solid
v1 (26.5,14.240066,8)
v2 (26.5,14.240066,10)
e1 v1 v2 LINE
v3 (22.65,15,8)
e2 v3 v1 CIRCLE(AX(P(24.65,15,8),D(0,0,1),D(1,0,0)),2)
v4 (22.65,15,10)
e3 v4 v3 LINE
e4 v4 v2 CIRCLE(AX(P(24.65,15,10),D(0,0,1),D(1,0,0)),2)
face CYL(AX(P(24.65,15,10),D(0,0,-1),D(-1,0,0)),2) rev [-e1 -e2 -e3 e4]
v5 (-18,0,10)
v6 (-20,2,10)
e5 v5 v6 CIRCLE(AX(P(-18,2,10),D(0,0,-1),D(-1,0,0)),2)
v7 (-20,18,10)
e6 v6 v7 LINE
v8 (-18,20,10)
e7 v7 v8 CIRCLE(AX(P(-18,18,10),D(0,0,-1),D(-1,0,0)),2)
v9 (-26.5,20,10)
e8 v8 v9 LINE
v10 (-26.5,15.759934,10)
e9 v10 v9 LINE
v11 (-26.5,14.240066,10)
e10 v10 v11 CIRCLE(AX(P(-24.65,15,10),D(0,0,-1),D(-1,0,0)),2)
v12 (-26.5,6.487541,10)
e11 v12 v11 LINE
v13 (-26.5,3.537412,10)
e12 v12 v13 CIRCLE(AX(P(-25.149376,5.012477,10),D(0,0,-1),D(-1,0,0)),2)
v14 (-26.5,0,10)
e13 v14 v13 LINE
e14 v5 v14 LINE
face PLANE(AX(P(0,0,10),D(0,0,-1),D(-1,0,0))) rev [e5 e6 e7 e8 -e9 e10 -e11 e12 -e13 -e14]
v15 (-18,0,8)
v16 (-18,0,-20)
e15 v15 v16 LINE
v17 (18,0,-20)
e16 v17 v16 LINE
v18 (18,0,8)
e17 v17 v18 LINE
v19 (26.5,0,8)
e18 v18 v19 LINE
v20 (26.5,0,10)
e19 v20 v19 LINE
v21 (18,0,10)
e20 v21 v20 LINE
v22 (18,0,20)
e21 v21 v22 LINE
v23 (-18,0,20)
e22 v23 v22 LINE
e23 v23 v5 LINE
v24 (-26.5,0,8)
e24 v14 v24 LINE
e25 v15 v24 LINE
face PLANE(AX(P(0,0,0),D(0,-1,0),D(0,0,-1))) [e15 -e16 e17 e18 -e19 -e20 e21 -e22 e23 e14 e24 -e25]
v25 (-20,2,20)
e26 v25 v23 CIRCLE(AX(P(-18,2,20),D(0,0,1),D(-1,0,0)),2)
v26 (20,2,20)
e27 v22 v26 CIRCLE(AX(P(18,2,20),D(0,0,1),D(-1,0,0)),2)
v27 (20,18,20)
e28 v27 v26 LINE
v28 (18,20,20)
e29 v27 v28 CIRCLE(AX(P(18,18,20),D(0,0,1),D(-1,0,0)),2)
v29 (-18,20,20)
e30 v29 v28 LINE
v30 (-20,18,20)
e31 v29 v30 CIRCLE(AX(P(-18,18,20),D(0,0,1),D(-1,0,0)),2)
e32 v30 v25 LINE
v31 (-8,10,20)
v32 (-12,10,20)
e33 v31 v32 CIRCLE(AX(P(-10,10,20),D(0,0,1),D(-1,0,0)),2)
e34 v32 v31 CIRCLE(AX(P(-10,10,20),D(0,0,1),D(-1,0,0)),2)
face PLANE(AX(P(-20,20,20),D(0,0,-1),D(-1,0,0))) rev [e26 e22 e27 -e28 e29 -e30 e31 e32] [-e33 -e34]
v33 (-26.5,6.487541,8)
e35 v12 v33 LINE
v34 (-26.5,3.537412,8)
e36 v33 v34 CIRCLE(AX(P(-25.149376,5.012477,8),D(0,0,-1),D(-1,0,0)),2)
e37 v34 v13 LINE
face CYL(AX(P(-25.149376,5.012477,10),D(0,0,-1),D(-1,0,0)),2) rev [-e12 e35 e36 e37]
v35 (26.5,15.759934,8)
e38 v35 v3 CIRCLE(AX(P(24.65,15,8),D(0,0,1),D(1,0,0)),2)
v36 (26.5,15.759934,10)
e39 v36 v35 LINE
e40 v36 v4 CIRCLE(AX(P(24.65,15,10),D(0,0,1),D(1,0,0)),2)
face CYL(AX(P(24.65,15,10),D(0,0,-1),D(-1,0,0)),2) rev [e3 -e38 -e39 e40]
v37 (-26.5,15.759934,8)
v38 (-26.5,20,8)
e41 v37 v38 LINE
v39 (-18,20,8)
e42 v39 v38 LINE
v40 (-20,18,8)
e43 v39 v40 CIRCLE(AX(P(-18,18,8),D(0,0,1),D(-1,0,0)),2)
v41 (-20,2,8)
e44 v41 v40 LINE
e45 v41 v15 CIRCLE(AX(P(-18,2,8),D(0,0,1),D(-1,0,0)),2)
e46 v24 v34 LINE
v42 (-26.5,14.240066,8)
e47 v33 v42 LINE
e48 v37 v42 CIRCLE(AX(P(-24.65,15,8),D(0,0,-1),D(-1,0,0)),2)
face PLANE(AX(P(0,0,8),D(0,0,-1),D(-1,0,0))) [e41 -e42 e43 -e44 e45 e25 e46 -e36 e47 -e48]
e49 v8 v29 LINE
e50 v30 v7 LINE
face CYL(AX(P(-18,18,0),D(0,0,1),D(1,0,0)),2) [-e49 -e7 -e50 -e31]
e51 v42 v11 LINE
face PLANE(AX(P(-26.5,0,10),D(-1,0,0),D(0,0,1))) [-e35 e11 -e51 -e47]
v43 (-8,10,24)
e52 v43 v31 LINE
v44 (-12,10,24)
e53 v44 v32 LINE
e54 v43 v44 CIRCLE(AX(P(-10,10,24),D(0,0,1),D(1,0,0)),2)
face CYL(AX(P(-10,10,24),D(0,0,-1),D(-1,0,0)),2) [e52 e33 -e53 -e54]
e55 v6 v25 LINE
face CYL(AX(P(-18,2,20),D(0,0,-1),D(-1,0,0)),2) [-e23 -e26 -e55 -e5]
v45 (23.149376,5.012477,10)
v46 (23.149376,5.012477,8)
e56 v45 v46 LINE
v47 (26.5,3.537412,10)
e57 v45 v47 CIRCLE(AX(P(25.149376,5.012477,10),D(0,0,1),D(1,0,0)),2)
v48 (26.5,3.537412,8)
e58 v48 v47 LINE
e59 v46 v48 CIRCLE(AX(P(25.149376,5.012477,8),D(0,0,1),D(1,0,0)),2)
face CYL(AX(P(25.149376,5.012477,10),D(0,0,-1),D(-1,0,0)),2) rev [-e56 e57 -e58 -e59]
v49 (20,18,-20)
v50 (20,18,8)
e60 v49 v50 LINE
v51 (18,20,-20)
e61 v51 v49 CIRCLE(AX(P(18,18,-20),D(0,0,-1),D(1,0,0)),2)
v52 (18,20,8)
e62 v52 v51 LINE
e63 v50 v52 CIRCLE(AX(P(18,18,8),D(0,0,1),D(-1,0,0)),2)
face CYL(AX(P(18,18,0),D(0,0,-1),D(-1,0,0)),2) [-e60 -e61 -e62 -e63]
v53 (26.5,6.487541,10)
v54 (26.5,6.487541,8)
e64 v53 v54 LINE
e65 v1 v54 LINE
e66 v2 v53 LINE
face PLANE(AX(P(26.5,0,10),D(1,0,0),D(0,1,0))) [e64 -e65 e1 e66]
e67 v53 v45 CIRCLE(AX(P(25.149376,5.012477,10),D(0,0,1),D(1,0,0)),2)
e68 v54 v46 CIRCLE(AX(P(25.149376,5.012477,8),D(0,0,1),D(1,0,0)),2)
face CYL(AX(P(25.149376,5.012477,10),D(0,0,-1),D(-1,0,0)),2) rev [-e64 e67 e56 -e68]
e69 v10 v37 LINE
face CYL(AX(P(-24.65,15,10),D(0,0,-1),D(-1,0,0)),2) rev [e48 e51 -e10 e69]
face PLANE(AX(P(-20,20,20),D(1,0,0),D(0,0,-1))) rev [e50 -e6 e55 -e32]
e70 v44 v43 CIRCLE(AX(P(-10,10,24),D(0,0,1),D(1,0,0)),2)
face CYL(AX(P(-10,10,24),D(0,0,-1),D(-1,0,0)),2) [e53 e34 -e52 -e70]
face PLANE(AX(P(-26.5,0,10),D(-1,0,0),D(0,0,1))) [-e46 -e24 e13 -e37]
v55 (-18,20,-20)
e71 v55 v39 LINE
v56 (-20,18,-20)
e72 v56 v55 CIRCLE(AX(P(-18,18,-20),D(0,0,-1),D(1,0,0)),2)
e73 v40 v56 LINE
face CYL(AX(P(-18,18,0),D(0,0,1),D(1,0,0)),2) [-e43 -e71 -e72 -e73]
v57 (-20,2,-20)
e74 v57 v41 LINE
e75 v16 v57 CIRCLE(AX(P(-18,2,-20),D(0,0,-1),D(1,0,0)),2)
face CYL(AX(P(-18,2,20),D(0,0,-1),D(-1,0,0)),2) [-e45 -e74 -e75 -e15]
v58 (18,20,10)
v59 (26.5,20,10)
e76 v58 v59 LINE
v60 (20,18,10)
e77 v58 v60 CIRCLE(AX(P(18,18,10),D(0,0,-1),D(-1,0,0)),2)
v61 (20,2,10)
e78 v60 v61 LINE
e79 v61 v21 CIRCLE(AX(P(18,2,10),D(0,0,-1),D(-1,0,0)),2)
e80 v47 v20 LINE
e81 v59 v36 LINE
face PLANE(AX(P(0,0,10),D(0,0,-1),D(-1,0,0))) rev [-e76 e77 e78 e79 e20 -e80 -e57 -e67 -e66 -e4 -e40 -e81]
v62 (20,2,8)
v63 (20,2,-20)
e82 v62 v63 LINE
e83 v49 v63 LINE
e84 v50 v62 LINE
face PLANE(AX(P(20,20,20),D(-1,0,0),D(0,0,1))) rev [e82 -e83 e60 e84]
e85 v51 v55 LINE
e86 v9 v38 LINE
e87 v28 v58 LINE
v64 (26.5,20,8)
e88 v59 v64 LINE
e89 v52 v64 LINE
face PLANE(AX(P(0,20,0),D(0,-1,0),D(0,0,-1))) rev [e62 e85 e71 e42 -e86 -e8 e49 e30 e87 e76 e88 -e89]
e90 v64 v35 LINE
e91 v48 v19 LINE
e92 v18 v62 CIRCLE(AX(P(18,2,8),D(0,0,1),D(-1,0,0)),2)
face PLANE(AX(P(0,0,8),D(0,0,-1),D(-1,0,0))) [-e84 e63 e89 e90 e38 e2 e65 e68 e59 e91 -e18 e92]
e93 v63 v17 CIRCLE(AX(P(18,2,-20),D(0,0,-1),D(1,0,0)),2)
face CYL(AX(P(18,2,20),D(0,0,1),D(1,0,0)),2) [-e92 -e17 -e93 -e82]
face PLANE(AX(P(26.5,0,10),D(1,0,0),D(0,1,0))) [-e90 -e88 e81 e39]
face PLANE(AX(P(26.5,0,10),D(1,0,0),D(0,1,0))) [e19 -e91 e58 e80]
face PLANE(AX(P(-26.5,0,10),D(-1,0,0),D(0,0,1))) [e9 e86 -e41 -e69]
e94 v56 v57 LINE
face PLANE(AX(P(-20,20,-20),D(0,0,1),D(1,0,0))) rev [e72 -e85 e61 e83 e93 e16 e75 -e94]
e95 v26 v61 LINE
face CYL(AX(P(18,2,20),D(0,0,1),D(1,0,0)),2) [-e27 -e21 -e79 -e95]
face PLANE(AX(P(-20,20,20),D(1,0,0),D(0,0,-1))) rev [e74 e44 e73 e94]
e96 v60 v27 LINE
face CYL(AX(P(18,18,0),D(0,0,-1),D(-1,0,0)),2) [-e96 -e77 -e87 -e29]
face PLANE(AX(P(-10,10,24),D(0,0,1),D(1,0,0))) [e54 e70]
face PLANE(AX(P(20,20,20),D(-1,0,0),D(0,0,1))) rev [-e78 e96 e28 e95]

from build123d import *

# Parameters (mm, degrees)
SKETCH1_W           = 40
SKETCH1_H           = 40
BOSS_EXTRUDE1_DEPTH = 20
SKETCH2_W           = 6.5
SKETCH2_H           = 20
BOSS_EXTRUDE2_DEPTH = 2
SKETCH3_R           = 2
CUT_EXTRUDE1_DEPTH  = 2
SKETCH4_R           = 2
BOSS_EXTRUDE3_DEPTH = 4
FILLET1_R           = 2


with BuildPart() as part:
    # Sketch1 → Boss-Extrude1 (new body)
    with BuildSketch(Plane(origin=(0, 0, 0), x_dir=(1, 0, 0), z_dir=(0, 1, 0))):
        Rectangle(SKETCH1_W, SKETCH1_H)
    extrude(amount=BOSS_EXTRUDE1_DEPTH)

    # Sketch2 → Boss-Extrude2 (add)
    with BuildSketch(Plane(origin=(0, 0, 8), x_dir=(-1, 0, 0), z_dir=(0, 0, -1))):
        with Locations((23.25, 10)):
            Rectangle(SKETCH2_W, SKETCH2_H)
        with Locations((-23.25, 10)):
            Rectangle(SKETCH2_W, SKETCH2_H)
    extrude(amount=-BOSS_EXTRUDE2_DEPTH)

    # Sketch3 → Cut-Extrude1 (cut)
    with BuildSketch(Plane(origin=(0, 0, 8), x_dir=(-1, 0, 0), z_dir=(0, 0, -1))):
        with Locations((25.149376169, 5.012476611)):
            Circle(SKETCH3_R)
        with Locations((24.65, 15)):
            Circle(SKETCH3_R)
    cut_extrude1 = extrude(amount=-CUT_EXTRUDE1_DEPTH, mode=Mode.SUBTRACT)

    # Mirror2: Cut-Extrude1 across plane
    add(cut_extrude1.mirror(Plane.ZY), mode=Mode.SUBTRACT)

    # Sketch4 → Boss-Extrude3 (add)
    with BuildSketch(Plane.XY.offset(20)):
        with Locations(Location((-10, 10, 0), (0, 0, 180))):
            Circle(SKETCH4_R)
    extrude(amount=BOSS_EXTRUDE3_DEPTH)

    # Fillet1
    fillet1_edges = [part.edges().sort_by_distance(p)[0] for p in [
        (20, 20, -6),
        (20, 20, 15),
        (20, 0, -6),
        (20, 0, 15),
        (-20, 0, 15),
        (-20, 0, -6),
        (-20, 20, 15),
        (-20, 20, -6),
    ]]
    fillet(fillet1_edges, radius=FILLET1_R)


solid = part.part
